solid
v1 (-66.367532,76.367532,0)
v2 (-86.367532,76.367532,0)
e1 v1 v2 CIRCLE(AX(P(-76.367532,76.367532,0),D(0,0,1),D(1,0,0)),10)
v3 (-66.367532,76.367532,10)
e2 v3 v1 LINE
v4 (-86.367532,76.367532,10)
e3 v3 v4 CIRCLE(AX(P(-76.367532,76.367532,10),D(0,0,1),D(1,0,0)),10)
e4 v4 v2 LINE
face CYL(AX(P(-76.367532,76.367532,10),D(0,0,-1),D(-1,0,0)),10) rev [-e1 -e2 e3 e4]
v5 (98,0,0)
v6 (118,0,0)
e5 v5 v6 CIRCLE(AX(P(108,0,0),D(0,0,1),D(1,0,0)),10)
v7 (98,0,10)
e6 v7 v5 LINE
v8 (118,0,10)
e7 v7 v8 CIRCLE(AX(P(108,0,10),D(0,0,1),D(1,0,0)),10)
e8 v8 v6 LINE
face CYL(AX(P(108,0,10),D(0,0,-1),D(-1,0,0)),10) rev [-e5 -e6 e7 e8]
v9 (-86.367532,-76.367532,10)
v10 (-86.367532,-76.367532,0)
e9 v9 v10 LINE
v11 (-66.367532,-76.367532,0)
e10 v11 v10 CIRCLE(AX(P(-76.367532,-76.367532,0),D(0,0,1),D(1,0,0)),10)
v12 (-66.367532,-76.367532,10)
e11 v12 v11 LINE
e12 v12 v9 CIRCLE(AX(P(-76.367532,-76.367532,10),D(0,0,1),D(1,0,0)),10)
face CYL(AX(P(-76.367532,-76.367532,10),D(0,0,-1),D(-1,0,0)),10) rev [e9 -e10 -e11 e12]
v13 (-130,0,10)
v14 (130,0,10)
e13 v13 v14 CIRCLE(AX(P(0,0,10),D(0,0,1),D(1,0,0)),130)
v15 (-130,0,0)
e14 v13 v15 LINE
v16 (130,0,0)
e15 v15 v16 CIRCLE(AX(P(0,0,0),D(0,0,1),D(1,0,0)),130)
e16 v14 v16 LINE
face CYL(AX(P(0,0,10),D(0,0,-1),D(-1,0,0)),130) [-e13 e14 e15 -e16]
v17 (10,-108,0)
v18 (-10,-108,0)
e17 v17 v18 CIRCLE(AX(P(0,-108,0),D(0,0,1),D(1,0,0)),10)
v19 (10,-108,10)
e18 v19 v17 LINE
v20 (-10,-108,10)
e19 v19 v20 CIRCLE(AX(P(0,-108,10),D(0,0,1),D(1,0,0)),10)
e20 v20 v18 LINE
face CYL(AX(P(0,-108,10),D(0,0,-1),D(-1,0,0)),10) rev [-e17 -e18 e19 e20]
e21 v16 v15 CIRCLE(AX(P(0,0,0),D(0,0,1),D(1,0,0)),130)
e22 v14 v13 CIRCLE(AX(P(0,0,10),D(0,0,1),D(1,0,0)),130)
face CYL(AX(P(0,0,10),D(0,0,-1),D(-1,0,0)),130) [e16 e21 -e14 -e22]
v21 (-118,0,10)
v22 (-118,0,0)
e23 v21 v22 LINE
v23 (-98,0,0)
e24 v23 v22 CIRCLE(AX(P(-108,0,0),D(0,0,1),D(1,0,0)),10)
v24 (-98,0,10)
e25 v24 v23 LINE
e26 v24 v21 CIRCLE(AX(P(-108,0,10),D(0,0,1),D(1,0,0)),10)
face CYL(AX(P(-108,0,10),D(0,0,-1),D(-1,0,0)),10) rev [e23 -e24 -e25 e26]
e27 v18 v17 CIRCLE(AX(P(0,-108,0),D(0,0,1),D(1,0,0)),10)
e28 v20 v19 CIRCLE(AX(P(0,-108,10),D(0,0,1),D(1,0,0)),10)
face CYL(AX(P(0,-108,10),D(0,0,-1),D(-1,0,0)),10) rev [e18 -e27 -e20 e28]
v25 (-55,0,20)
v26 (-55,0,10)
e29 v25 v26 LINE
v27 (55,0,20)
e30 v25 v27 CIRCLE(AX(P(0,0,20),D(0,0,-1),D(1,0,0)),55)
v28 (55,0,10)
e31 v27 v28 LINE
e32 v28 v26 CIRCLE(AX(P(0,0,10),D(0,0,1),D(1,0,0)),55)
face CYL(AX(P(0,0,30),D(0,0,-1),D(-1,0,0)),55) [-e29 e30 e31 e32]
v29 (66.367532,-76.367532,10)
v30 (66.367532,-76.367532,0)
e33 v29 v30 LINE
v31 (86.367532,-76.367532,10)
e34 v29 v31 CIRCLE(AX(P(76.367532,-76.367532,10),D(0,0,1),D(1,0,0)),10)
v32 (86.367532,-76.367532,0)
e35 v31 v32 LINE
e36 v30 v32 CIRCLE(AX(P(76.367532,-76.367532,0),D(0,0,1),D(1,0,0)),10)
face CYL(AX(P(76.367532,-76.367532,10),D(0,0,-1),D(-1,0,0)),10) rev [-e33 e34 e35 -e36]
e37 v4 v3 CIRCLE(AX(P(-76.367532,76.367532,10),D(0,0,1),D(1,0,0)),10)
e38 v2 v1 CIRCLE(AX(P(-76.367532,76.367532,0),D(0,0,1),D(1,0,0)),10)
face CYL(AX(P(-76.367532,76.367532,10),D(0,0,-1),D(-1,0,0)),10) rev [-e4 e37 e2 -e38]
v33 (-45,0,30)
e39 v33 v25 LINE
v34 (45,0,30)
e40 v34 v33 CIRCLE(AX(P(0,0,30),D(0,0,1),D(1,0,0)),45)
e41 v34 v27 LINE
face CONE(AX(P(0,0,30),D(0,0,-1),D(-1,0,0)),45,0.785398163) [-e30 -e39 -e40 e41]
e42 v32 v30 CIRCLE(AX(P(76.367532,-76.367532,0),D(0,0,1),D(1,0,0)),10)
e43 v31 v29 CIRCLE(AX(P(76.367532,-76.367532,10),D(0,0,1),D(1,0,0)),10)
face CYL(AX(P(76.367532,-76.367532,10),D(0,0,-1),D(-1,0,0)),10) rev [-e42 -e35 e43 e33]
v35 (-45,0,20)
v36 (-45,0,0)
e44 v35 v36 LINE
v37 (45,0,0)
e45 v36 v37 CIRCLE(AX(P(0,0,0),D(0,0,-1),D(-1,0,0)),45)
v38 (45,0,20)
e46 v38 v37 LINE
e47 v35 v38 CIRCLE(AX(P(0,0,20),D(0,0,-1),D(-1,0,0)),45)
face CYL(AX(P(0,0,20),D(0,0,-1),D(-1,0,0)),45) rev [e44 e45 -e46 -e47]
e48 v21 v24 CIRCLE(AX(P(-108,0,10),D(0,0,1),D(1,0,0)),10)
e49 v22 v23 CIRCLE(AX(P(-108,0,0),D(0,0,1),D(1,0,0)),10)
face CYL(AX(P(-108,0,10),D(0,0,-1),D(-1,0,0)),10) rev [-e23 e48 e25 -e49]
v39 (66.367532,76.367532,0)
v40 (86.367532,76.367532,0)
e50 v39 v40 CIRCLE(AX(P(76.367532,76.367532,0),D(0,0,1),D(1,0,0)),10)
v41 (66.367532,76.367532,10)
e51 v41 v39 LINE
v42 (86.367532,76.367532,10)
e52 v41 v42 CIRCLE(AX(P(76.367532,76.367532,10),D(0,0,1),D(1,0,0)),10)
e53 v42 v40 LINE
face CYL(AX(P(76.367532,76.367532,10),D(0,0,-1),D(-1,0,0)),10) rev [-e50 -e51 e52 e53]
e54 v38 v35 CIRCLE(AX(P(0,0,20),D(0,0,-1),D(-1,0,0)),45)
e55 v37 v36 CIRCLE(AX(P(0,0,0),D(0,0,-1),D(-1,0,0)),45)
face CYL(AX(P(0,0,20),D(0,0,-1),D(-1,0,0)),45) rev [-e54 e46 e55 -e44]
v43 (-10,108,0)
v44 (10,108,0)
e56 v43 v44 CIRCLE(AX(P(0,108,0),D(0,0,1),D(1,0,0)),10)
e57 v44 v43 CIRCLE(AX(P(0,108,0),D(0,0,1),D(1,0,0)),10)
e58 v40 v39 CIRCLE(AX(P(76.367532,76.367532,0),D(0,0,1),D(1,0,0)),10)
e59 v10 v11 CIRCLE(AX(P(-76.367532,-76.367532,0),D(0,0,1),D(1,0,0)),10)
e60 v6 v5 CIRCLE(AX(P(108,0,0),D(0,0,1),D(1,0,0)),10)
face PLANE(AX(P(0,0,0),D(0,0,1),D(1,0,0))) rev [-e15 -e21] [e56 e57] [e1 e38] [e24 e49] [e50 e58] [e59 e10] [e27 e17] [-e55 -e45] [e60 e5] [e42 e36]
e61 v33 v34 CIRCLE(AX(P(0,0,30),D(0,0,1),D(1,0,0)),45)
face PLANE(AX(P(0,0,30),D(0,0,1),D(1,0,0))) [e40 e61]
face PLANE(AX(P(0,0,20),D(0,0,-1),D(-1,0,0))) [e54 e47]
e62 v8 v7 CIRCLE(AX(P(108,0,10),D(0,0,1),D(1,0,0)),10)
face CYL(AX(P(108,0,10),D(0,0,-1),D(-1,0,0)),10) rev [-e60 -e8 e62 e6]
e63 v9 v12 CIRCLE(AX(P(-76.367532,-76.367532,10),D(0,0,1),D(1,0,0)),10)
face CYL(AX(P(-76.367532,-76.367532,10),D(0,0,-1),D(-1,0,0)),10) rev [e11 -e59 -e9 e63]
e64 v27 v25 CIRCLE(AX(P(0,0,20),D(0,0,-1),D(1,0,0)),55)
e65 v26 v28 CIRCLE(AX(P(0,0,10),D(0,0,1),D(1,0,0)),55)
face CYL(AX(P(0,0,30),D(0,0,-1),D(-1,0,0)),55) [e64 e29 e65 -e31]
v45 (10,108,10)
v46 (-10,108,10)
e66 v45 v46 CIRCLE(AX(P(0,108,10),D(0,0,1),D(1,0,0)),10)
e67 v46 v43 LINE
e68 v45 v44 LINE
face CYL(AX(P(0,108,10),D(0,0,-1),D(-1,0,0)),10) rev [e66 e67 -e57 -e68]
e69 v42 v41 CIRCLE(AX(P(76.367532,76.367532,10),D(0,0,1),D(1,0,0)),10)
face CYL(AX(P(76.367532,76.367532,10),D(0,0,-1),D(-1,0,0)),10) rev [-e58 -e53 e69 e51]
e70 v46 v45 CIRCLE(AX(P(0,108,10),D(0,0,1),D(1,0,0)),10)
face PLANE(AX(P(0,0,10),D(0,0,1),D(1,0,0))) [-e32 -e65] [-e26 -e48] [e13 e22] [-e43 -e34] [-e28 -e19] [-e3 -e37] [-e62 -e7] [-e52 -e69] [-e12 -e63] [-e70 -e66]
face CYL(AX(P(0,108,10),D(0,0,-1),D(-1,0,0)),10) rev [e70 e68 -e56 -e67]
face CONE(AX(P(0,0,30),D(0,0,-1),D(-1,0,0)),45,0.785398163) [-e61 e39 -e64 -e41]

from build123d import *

# Parameters (mm, degrees)
SKETCH_1_R          = 130
SKETCH_1_R_2        = 10
EXTRUDE_1_DEPTH     = 10
SKETCH_2_R          = 55
EXTRUDE_2_DEPTH     = 20
SKETCH_3_R          = 45
CUT_EXTRUDE_1_DEPTH = 20
CHAMFER_1_SIZE      = 10


with BuildPart() as part:
    # 草图1 → 凸台-拉伸1 (new body)
    with BuildSketch(Plane.XY):
        Circle(SKETCH_1_R)
        with Locations((0, 108)):
            Circle(SKETCH_1_R_2, mode=Mode.SUBTRACT)
        with Locations((76.367532368, 76.367532368)):
            Circle(SKETCH_1_R_2, mode=Mode.SUBTRACT)
        with Locations((108, 0)):
            Circle(SKETCH_1_R_2, mode=Mode.SUBTRACT)
        with Locations((76.367532368, -76.367532368)):
            Circle(SKETCH_1_R_2, mode=Mode.SUBTRACT)
        with Locations((0, -108)):
            Circle(SKETCH_1_R_2, mode=Mode.SUBTRACT)
        with Locations((-76.367532368, -76.367532368)):
            Circle(SKETCH_1_R_2, mode=Mode.SUBTRACT)
        with Locations((-108, 0)):
            Circle(SKETCH_1_R_2, mode=Mode.SUBTRACT)
        with Locations((-76.367532368, 76.367532368)):
            Circle(SKETCH_1_R_2, mode=Mode.SUBTRACT)
    extrude(amount=EXTRUDE_1_DEPTH)

    # 草图2 → 凸台-拉伸2 (add)
    with BuildSketch(Plane.XY.offset(10)):
        Circle(SKETCH_2_R)
    extrude(amount=EXTRUDE_2_DEPTH)

    # 草图3 → 切除-拉伸1 (cut)
    with BuildSketch(Plane(origin=(0, 0, 0), x_dir=(-1, 0, 0), z_dir=(0, 0, -1))):
        Circle(SKETCH_3_R)
    extrude(amount=-CUT_EXTRUDE_1_DEPTH, mode=Mode.SUBTRACT)

    # 倒角1
    chamfer_1_edges = [part.edges().sort_by_distance(p)[0] for p in [
        (-55, 0, 30),
    ]]
    chamfer(chamfer_1_edges, length=CHAMFER_1_SIZE)


solid = part.part
